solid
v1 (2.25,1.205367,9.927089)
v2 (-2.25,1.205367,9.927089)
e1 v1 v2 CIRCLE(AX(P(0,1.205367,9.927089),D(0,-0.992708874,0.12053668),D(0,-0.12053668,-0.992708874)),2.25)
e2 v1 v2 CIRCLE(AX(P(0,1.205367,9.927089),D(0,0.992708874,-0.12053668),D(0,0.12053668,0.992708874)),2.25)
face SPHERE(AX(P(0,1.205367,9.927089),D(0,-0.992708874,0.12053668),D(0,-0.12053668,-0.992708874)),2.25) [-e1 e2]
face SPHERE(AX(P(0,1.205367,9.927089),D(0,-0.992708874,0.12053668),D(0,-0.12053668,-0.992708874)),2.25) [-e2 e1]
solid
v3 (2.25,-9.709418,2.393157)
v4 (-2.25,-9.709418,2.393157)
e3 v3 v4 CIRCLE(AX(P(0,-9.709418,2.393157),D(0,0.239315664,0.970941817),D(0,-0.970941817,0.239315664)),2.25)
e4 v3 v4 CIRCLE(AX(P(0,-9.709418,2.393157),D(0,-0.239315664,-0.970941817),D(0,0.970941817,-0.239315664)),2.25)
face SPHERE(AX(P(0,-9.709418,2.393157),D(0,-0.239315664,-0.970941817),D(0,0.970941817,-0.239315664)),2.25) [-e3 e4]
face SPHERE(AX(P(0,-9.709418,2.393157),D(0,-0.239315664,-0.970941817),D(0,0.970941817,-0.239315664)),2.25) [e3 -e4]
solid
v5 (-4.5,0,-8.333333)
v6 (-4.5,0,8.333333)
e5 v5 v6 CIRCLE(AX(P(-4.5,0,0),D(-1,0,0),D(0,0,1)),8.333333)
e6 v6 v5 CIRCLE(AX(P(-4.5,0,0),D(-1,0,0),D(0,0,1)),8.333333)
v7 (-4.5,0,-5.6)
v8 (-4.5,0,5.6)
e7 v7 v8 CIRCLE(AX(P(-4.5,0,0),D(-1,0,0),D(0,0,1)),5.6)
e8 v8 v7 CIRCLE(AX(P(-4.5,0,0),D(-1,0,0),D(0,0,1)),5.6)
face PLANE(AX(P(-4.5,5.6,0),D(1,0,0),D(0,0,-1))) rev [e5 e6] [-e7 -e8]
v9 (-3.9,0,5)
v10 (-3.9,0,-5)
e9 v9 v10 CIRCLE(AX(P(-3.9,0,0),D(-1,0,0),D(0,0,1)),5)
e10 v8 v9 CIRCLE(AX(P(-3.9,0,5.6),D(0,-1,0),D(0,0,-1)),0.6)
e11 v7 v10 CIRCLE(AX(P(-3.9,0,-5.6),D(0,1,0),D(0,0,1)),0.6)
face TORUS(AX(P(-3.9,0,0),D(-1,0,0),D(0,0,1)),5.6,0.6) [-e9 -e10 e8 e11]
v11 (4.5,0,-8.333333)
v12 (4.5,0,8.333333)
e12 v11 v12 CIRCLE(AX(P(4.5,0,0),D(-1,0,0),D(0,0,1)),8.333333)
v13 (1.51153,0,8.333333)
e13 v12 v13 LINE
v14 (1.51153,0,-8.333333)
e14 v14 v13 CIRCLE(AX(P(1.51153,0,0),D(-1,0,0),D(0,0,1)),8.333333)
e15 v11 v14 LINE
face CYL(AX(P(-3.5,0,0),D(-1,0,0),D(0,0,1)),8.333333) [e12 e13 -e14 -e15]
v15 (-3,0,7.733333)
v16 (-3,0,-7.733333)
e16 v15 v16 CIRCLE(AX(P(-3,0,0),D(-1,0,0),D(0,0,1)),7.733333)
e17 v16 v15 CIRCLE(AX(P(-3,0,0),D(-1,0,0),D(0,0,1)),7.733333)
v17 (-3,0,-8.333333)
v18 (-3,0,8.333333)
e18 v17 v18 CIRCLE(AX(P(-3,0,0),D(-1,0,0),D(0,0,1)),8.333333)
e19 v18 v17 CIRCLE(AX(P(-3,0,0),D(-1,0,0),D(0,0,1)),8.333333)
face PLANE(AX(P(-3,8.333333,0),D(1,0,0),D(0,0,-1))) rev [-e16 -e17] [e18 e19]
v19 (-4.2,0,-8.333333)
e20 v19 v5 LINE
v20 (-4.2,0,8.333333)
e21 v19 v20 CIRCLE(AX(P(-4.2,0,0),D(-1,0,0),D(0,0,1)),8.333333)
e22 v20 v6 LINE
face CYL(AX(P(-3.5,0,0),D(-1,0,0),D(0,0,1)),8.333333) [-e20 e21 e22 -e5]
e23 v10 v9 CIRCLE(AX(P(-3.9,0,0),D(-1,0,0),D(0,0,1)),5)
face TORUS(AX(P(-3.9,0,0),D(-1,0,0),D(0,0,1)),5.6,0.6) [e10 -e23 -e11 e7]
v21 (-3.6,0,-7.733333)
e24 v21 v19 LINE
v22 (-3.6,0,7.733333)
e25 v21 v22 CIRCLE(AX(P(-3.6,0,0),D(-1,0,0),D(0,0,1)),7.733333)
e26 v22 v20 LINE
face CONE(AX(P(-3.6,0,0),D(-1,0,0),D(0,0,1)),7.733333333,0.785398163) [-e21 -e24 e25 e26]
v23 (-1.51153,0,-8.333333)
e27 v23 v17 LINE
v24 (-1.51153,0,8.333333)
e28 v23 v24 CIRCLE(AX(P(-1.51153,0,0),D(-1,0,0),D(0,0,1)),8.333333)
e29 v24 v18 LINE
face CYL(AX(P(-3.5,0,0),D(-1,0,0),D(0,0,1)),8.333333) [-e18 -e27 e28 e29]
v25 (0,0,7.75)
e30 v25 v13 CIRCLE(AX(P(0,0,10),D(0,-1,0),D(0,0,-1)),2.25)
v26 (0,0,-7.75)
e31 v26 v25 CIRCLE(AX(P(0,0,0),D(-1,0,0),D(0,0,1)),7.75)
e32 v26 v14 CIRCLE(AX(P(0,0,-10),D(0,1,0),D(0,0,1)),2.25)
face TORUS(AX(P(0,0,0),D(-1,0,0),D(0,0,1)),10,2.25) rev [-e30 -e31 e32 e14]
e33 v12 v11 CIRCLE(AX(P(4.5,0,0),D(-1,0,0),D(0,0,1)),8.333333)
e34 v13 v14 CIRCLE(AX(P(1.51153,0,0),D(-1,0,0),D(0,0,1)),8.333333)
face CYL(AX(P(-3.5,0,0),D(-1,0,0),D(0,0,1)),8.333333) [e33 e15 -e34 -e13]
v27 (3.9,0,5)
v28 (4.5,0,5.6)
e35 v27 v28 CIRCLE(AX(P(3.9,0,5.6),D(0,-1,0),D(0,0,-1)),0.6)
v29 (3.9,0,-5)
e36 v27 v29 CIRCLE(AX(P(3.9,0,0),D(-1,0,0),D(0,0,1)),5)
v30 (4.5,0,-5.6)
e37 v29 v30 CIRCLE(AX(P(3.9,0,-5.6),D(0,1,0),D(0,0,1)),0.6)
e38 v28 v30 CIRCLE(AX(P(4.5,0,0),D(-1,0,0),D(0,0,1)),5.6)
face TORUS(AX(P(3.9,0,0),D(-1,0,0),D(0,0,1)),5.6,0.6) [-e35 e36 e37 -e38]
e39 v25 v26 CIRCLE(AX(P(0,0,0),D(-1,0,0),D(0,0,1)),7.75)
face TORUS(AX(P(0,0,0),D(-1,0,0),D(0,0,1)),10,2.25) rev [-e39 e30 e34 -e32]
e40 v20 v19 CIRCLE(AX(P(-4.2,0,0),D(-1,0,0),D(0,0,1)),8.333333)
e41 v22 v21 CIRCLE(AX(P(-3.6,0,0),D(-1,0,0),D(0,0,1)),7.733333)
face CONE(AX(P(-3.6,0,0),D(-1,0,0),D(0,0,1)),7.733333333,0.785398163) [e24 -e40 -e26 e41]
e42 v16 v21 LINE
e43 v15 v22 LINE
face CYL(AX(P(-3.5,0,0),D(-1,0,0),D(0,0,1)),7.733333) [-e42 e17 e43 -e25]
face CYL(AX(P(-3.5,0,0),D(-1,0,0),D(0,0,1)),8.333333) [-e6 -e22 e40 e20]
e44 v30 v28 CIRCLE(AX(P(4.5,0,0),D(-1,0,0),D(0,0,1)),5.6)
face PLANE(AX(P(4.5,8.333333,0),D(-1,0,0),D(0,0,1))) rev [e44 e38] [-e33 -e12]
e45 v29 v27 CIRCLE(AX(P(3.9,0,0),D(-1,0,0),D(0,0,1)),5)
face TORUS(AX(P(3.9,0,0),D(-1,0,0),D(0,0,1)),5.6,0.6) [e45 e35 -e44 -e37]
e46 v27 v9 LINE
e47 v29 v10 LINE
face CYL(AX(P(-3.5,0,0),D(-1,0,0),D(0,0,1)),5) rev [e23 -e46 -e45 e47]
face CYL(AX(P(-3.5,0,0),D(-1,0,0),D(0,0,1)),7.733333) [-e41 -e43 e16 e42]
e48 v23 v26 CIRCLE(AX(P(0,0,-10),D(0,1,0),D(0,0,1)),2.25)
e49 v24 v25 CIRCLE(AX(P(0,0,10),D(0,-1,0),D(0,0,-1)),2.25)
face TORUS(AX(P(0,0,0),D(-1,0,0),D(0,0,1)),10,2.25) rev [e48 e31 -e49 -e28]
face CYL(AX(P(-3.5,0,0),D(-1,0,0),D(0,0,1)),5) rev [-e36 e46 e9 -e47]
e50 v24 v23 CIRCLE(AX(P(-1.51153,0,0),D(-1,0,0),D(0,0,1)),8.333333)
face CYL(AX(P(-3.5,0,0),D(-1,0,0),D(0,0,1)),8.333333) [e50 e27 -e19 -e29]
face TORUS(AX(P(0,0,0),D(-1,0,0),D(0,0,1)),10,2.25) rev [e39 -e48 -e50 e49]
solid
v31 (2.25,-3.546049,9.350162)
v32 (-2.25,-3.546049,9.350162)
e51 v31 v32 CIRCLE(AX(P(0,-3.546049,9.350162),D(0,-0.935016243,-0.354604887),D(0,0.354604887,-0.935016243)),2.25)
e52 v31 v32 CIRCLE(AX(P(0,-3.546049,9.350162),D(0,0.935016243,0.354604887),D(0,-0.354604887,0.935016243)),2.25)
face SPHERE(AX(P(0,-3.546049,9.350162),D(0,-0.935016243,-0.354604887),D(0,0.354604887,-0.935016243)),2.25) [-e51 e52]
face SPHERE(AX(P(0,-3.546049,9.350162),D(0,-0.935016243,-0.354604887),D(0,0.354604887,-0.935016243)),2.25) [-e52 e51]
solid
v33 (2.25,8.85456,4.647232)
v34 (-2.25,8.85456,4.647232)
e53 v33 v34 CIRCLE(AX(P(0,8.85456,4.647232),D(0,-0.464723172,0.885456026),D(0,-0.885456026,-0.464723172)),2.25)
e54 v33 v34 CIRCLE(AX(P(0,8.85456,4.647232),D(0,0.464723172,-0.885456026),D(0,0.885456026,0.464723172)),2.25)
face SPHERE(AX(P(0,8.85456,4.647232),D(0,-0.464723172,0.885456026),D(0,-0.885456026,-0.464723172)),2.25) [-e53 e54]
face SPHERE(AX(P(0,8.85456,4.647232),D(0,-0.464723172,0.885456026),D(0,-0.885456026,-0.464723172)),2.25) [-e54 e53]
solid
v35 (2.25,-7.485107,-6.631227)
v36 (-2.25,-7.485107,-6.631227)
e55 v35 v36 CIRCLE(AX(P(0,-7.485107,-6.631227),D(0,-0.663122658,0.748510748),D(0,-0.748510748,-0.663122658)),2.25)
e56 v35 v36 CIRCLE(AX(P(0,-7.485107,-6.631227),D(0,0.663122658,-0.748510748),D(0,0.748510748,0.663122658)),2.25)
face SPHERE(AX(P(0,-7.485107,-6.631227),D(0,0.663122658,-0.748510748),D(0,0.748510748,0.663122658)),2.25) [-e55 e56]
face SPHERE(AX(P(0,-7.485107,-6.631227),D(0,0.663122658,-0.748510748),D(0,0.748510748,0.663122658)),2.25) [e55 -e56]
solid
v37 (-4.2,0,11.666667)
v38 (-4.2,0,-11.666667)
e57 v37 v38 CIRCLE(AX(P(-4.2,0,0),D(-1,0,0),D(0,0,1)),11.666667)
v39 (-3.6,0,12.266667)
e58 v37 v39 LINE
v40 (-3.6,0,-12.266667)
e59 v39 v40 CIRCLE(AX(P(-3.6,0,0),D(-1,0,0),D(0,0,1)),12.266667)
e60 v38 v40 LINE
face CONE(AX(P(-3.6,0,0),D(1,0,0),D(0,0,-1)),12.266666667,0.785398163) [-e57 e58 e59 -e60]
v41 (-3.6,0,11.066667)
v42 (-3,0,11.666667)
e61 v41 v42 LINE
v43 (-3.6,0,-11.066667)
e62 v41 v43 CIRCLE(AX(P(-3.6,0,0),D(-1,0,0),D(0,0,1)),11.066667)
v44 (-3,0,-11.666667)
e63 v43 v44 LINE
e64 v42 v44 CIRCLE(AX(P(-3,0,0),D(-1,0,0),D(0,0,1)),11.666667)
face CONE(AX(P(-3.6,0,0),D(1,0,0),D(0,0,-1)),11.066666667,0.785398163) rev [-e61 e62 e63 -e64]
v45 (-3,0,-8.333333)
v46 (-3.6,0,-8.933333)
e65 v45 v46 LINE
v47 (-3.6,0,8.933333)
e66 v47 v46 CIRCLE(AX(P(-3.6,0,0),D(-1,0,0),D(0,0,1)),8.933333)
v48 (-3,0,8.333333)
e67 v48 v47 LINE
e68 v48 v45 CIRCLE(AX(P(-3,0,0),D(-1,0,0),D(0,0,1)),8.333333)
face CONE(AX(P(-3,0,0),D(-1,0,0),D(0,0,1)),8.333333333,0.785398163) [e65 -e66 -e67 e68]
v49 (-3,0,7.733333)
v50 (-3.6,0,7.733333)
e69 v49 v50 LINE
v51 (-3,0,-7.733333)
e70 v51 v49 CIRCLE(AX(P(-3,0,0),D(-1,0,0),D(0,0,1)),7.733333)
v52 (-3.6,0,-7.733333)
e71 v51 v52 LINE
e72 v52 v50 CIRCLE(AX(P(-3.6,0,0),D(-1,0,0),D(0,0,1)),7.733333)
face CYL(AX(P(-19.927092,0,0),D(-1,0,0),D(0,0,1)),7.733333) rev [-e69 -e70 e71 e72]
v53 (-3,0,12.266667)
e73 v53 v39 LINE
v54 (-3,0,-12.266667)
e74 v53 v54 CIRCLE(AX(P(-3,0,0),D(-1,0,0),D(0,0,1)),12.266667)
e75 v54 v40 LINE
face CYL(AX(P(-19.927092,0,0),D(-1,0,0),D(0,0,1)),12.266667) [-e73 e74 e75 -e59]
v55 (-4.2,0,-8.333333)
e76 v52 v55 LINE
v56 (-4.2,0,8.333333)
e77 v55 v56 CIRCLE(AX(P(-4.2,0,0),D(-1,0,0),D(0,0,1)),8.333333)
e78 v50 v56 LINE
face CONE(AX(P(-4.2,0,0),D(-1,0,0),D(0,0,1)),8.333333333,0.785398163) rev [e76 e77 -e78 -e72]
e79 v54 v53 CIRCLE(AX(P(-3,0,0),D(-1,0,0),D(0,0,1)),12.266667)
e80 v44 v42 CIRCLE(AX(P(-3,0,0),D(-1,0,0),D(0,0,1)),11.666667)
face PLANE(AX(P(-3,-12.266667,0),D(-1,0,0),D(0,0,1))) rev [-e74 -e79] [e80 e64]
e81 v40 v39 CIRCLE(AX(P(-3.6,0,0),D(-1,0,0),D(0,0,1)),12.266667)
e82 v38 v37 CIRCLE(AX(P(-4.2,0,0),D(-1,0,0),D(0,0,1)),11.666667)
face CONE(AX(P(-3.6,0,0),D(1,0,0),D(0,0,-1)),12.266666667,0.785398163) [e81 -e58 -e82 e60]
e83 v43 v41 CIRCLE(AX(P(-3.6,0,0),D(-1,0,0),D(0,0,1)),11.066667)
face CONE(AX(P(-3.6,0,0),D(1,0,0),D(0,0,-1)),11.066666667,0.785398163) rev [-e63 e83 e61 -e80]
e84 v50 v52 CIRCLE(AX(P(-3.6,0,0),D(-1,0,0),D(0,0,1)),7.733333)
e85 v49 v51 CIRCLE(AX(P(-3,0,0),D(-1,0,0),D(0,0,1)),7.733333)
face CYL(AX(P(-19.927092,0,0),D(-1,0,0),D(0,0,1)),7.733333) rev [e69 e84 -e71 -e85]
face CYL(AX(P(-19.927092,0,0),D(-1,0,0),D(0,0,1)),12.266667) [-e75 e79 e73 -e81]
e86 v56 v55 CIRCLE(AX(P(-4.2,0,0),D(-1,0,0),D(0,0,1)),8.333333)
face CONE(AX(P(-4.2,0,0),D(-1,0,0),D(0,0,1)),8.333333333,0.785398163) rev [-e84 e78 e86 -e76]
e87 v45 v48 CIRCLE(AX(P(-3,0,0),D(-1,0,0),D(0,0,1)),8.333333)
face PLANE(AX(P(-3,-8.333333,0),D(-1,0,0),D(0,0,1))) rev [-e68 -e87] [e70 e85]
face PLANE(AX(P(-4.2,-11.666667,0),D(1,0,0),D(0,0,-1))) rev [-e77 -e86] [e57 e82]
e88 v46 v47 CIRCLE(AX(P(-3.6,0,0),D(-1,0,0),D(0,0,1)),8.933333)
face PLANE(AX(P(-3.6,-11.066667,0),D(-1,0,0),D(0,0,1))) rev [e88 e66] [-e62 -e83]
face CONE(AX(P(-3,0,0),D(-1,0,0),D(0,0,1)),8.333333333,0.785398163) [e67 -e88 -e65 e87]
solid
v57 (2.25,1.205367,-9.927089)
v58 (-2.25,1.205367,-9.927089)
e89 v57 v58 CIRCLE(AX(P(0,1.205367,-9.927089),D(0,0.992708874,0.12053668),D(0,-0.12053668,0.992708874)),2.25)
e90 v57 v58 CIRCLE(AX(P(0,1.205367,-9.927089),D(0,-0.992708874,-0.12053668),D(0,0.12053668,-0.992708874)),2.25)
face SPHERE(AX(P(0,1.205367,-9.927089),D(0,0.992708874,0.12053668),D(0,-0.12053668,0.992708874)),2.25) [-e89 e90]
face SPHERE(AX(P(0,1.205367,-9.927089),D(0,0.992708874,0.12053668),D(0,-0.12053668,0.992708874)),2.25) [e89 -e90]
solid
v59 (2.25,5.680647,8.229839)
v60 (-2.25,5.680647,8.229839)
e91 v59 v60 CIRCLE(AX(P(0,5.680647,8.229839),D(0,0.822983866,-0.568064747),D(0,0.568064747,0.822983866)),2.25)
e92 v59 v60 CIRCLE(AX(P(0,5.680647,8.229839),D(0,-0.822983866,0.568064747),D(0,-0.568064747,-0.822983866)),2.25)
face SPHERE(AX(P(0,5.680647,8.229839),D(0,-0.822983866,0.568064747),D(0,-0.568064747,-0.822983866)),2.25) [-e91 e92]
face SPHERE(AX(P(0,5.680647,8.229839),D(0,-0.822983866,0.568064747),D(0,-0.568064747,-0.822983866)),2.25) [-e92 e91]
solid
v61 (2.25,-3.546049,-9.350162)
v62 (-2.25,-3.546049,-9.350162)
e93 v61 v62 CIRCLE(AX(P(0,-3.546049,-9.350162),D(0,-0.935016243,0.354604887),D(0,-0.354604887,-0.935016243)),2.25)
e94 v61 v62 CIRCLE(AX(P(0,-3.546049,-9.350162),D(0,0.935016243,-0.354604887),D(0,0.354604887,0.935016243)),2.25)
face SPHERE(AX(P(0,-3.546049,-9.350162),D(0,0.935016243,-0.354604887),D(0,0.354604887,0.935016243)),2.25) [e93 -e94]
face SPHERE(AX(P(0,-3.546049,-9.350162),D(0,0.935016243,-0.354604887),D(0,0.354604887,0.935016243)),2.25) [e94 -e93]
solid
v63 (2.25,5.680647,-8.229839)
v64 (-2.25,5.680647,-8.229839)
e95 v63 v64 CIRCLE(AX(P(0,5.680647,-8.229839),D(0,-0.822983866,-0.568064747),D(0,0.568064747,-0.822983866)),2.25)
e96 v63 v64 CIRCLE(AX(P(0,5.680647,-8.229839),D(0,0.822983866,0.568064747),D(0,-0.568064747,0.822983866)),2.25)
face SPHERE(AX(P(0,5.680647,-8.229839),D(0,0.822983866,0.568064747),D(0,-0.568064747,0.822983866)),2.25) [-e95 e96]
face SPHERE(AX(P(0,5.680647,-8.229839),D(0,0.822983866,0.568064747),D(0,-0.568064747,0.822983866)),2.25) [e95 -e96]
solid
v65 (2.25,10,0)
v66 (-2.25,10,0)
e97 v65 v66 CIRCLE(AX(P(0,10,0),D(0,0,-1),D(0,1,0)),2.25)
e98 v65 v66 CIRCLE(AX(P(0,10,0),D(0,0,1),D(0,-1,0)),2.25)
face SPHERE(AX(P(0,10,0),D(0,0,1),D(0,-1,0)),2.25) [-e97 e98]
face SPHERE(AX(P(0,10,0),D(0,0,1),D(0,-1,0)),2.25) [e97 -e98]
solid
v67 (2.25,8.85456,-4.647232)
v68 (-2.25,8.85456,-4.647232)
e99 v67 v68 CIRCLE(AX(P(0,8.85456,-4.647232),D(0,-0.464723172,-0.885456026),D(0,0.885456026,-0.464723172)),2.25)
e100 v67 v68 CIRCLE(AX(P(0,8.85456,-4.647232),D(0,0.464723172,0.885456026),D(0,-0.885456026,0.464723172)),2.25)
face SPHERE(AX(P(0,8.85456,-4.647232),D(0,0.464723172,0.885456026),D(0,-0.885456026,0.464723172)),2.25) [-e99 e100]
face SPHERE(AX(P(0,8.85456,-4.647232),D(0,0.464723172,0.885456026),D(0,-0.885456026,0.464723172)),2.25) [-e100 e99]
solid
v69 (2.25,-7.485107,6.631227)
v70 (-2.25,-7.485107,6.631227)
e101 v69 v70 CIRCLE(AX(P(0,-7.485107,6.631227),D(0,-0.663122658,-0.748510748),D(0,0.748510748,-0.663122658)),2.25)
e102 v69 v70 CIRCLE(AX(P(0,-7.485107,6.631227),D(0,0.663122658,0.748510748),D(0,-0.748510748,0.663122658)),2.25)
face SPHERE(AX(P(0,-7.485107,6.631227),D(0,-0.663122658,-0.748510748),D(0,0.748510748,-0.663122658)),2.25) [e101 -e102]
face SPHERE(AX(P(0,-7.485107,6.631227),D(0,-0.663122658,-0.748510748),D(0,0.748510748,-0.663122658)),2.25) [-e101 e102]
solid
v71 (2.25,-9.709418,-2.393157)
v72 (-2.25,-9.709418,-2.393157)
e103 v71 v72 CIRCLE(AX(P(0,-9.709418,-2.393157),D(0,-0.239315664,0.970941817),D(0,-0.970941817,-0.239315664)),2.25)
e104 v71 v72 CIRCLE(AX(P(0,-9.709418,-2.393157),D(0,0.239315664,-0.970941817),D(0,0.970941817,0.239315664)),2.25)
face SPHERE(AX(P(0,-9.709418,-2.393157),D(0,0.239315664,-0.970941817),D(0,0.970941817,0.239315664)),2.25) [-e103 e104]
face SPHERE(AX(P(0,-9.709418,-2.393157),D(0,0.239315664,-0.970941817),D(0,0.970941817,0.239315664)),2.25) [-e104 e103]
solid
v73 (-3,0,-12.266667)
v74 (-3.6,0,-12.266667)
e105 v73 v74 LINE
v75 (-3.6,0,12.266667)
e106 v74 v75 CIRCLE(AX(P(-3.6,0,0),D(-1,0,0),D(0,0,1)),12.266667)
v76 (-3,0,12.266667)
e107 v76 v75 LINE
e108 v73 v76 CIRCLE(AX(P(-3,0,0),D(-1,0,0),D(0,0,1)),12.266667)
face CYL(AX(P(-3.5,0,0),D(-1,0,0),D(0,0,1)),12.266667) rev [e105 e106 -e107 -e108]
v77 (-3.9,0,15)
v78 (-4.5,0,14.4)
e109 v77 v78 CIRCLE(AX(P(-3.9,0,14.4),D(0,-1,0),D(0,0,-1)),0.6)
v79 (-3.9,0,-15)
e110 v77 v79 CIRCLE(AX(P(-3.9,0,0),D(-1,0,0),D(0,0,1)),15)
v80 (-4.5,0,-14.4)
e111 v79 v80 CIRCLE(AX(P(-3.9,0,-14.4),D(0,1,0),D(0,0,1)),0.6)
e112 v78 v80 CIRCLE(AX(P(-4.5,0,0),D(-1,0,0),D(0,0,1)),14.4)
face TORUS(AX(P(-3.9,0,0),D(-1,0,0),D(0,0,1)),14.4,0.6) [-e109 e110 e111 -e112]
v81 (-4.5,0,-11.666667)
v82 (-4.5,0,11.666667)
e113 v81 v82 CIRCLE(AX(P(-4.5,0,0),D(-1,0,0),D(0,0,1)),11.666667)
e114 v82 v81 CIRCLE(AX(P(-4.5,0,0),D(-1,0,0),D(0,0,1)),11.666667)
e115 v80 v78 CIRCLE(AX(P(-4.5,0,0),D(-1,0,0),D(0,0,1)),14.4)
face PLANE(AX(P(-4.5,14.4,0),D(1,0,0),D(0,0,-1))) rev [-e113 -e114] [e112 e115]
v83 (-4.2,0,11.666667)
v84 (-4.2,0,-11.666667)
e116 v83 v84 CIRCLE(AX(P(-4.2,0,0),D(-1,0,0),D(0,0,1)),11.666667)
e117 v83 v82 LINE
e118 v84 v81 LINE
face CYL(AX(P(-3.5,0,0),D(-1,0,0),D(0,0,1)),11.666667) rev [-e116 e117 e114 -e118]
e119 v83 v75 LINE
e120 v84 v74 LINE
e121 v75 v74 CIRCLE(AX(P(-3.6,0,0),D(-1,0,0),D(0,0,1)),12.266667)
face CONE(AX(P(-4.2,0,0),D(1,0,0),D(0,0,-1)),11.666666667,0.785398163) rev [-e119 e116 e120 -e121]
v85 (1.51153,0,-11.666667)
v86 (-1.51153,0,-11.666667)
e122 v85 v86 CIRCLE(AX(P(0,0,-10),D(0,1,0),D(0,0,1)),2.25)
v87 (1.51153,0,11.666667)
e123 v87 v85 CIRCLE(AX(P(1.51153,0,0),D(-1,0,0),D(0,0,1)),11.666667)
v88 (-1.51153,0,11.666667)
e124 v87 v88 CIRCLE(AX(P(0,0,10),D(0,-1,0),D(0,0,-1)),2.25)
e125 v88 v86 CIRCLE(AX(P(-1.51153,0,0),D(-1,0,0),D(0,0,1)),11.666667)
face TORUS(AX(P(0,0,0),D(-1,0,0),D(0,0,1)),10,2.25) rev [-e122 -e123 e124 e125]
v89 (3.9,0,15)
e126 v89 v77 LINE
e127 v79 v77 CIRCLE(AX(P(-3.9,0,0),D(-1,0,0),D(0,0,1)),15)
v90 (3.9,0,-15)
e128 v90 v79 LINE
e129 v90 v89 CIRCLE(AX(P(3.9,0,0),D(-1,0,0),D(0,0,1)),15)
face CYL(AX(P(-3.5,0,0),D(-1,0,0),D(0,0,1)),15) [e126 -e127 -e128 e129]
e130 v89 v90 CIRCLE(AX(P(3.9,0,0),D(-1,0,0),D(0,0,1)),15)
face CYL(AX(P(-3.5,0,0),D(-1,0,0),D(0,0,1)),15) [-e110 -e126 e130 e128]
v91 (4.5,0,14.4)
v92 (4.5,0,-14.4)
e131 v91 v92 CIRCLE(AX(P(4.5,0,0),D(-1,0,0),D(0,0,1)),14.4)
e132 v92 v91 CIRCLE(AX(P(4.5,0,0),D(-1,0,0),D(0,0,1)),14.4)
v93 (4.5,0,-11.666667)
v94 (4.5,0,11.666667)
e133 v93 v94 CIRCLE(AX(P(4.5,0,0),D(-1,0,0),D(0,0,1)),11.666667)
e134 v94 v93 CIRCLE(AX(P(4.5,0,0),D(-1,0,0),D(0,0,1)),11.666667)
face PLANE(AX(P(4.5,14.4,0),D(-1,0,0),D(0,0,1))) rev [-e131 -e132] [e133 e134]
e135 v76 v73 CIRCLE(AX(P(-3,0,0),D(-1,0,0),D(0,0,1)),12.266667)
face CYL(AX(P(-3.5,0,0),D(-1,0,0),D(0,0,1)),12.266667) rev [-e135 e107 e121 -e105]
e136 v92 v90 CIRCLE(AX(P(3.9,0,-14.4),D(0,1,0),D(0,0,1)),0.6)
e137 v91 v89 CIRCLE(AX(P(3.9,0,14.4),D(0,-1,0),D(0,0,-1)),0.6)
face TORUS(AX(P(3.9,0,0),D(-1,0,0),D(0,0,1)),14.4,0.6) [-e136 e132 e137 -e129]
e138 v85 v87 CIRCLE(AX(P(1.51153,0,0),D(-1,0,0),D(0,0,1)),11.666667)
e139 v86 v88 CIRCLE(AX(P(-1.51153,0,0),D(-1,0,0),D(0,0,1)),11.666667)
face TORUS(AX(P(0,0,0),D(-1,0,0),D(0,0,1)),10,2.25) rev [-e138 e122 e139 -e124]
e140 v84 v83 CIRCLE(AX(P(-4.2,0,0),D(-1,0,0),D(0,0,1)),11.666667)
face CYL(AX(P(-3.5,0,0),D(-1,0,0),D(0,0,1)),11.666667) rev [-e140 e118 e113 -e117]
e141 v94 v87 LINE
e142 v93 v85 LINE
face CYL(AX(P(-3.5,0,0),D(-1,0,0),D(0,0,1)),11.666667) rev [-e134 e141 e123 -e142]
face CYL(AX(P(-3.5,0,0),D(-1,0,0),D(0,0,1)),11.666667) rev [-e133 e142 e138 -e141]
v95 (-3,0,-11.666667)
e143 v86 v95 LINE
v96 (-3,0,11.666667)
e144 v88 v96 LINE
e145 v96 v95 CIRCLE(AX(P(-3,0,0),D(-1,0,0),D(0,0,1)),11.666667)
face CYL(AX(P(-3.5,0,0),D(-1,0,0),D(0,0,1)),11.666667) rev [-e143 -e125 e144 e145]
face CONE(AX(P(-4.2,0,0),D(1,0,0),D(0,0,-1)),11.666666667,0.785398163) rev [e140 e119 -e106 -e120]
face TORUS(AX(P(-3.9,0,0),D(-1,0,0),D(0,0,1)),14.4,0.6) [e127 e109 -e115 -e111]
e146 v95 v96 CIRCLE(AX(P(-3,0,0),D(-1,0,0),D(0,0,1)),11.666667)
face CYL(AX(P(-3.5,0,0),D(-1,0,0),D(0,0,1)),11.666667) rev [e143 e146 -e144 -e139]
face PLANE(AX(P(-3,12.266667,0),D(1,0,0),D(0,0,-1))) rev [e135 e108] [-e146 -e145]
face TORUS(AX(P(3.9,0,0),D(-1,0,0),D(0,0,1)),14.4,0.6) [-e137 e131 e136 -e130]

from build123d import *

# Parameters (mm, degrees)
PATTERN_CIRCULAR_5_COUNT = 13


with BuildPart() as part:
    # 草图2 → 旋转1 (revolve)
    with BuildSketch(Plane.XY, mode=Mode.PRIVATE) as revolve_1_sk:
        with BuildLine():
            Line((-4.2, 8.333333333), (-4.5, 8.333333333))
            Line((-4.5, 8.333333333), (-4.5, 7.733333333))
            Line((-4.5, 7.733333333), (-4.5, 5.6))
            ThreePointArc((-4.5, 5.6), (-4.324264069, 5.175735931), (-3.9, 5))
            Line((-3.9, 5), (3.9, 5))
            ThreePointArc((3.9, 5), (4.324264069, 5.175735931), (4.5, 5.6))
            Line((4.5, 5.6), (4.5, 7.733333333))
            Line((4.5, 7.733333333), (4.5, 8.333333333))
            Line((4.5, 8.333333333), (3.9, 8.333333333))
            Line((3.9, 8.333333333), (1.511529762, 8.333333333))
            ThreePointArc((1.511529762, 8.333333333), (0, 7.75), (-1.511529762, 8.333333333))
            Line((-1.511529762, 8.333333333), (-3, 8.333333333))
            Line((-3, 8.333333333), (-3, 7.733333333))
            Line((-3, 7.733333333), (-3.6, 7.733333333))
            Line((-3.6, 7.733333333), (-4.2, 8.333333333))
        make_face()
        with BuildLine():
            Line((-4.5, 11.666666667), (-4.2, 11.666666667))
            Line((-4.2, 11.666666667), (-3.6, 12.266666667))
            Line((-3.6, 12.266666667), (-3, 12.266666667))
            Line((-3, 12.266666667), (-3, 11.666666667))
            Line((-3, 11.666666667), (-1.511529762, 11.666666667))
            ThreePointArc((-1.511529762, 11.666666667), (0, 12.25), (1.511529762, 11.666666667))
            Line((1.511529762, 11.666666667), (4.5, 11.666666667))
            Line((4.5, 11.666666667), (4.5, 14.4))
            ThreePointArc((4.5, 14.4), (4.324264069, 14.824264069), (3.9, 15))
            Line((3.9, 15), (-3.9, 15))
            ThreePointArc((-3.9, 15), (-4.324264069, 14.824264069), (-4.5, 14.4))
            Line((-4.5, 14.4), (-4.5, 11.666666667))
        make_face()
    revolve(revolve_1_sk.sketch.rotate(Axis((-3.5, 0, 0), (1, 0, 0)), 90), axis=Axis((-3.5, 0, 0), (1, 0, 0)))


with BuildPart() as body_2:
    # 草图3 → 旋转2 (revolve)
    with BuildSketch(Plane.XY):
        with BuildLine():
            Line((-2.25, 10), (2.25, 10))
            ThreePointArc((2.25, 10), (0, 12.25), (-2.25, 10))
        make_face()
    revolve(axis=Axis((2.25, 10, 0), (1, 0, 0)))


with BuildPart() as body_3:
    # 草图4 → 旋转3 (revolve)
    with BuildSketch(Plane.XY, mode=Mode.PRIVATE) as revolve_3_sk:
        Polygon((-4.2, 11.666666667), (-4.2, 8.333333333), (-3.6, 7.733333333), (-3, 7.733333333), (-3, 8.333333333), (-3.6, 8.933333333), (-3.6, 11.066666667), (-3, 11.666666667), (-3, 12.266666667), (-3.6, 12.266666667), align=None)
    revolve(revolve_3_sk.sketch.rotate(Axis((-19.927092192, 0, 0), (1, 0, 0)), 90), axis=Axis((-19.927092192, 0, 0), (1, 0, 0)))


with BuildPart() as pattern_circular_5_1:
    # 阵列(圆周)5: pattern copy
    add(body_2.part.rotate(Axis((0, 0, 0), (1, 0, 0)), 1 * 360 / PATTERN_CIRCULAR_5_COUNT))


with BuildPart() as pattern_circular_5_2:
    # 阵列(圆周)5: pattern copy
    add(body_2.part.rotate(Axis((0, 0, 0), (1, 0, 0)), 2 * 360 / PATTERN_CIRCULAR_5_COUNT))


with BuildPart() as pattern_circular_5_3:
    # 阵列(圆周)5: pattern copy
    add(body_2.part.rotate(Axis((0, 0, 0), (1, 0, 0)), 3 * 360 / PATTERN_CIRCULAR_5_COUNT))


with BuildPart() as pattern_circular_5_4:
    # 阵列(圆周)5: pattern copy
    add(body_2.part.rotate(Axis((0, 0, 0), (1, 0, 0)), 4 * 360 / PATTERN_CIRCULAR_5_COUNT))


with BuildPart() as pattern_circular_5_5:
    # 阵列(圆周)5: pattern copy
    add(body_2.part.rotate(Axis((0, 0, 0), (1, 0, 0)), 5 * 360 / PATTERN_CIRCULAR_5_COUNT))


with BuildPart() as pattern_circular_5_6:
    # 阵列(圆周)5: pattern copy
    add(body_2.part.rotate(Axis((0, 0, 0), (1, 0, 0)), 6 * 360 / PATTERN_CIRCULAR_5_COUNT))


with BuildPart() as pattern_circular_5_7:
    # 阵列(圆周)5: pattern copy
    add(body_2.part.rotate(Axis((0, 0, 0), (1, 0, 0)), 7 * 360 / PATTERN_CIRCULAR_5_COUNT))


with BuildPart() as pattern_circular_5_8:
    # 阵列(圆周)5: pattern copy
    add(body_2.part.rotate(Axis((0, 0, 0), (1, 0, 0)), 8 * 360 / PATTERN_CIRCULAR_5_COUNT))


with BuildPart() as pattern_circular_5_9:
    # 阵列(圆周)5: pattern copy
    add(body_2.part.rotate(Axis((0, 0, 0), (1, 0, 0)), 9 * 360 / PATTERN_CIRCULAR_5_COUNT))


with BuildPart() as pattern_circular_5_10:
    # 阵列(圆周)5: pattern copy
    add(body_2.part.rotate(Axis((0, 0, 0), (1, 0, 0)), 10 * 360 / PATTERN_CIRCULAR_5_COUNT))


with BuildPart() as pattern_circular_5_11:
    # 阵列(圆周)5: pattern copy
    add(body_2.part.rotate(Axis((0, 0, 0), (1, 0, 0)), 11 * 360 / PATTERN_CIRCULAR_5_COUNT))


with BuildPart() as pattern_circular_5_12:
    # 阵列(圆周)5: pattern copy
    add(body_2.part.rotate(Axis((0, 0, 0), (1, 0, 0)), 12 * 360 / PATTERN_CIRCULAR_5_COUNT))


solid = Compound([part.part, body_2.part, body_3.part, pattern_circular_5_1.part, pattern_circular_5_2.part, pattern_circular_5_3.part, pattern_circular_5_4.part, pattern_circular_5_5.part, pattern_circular_5_6.part, pattern_circular_5_7.part, pattern_circular_5_8.part, pattern_circular_5_9.part, pattern_circular_5_10.part, pattern_circular_5_11.part, pattern_circular_5_12.part])
